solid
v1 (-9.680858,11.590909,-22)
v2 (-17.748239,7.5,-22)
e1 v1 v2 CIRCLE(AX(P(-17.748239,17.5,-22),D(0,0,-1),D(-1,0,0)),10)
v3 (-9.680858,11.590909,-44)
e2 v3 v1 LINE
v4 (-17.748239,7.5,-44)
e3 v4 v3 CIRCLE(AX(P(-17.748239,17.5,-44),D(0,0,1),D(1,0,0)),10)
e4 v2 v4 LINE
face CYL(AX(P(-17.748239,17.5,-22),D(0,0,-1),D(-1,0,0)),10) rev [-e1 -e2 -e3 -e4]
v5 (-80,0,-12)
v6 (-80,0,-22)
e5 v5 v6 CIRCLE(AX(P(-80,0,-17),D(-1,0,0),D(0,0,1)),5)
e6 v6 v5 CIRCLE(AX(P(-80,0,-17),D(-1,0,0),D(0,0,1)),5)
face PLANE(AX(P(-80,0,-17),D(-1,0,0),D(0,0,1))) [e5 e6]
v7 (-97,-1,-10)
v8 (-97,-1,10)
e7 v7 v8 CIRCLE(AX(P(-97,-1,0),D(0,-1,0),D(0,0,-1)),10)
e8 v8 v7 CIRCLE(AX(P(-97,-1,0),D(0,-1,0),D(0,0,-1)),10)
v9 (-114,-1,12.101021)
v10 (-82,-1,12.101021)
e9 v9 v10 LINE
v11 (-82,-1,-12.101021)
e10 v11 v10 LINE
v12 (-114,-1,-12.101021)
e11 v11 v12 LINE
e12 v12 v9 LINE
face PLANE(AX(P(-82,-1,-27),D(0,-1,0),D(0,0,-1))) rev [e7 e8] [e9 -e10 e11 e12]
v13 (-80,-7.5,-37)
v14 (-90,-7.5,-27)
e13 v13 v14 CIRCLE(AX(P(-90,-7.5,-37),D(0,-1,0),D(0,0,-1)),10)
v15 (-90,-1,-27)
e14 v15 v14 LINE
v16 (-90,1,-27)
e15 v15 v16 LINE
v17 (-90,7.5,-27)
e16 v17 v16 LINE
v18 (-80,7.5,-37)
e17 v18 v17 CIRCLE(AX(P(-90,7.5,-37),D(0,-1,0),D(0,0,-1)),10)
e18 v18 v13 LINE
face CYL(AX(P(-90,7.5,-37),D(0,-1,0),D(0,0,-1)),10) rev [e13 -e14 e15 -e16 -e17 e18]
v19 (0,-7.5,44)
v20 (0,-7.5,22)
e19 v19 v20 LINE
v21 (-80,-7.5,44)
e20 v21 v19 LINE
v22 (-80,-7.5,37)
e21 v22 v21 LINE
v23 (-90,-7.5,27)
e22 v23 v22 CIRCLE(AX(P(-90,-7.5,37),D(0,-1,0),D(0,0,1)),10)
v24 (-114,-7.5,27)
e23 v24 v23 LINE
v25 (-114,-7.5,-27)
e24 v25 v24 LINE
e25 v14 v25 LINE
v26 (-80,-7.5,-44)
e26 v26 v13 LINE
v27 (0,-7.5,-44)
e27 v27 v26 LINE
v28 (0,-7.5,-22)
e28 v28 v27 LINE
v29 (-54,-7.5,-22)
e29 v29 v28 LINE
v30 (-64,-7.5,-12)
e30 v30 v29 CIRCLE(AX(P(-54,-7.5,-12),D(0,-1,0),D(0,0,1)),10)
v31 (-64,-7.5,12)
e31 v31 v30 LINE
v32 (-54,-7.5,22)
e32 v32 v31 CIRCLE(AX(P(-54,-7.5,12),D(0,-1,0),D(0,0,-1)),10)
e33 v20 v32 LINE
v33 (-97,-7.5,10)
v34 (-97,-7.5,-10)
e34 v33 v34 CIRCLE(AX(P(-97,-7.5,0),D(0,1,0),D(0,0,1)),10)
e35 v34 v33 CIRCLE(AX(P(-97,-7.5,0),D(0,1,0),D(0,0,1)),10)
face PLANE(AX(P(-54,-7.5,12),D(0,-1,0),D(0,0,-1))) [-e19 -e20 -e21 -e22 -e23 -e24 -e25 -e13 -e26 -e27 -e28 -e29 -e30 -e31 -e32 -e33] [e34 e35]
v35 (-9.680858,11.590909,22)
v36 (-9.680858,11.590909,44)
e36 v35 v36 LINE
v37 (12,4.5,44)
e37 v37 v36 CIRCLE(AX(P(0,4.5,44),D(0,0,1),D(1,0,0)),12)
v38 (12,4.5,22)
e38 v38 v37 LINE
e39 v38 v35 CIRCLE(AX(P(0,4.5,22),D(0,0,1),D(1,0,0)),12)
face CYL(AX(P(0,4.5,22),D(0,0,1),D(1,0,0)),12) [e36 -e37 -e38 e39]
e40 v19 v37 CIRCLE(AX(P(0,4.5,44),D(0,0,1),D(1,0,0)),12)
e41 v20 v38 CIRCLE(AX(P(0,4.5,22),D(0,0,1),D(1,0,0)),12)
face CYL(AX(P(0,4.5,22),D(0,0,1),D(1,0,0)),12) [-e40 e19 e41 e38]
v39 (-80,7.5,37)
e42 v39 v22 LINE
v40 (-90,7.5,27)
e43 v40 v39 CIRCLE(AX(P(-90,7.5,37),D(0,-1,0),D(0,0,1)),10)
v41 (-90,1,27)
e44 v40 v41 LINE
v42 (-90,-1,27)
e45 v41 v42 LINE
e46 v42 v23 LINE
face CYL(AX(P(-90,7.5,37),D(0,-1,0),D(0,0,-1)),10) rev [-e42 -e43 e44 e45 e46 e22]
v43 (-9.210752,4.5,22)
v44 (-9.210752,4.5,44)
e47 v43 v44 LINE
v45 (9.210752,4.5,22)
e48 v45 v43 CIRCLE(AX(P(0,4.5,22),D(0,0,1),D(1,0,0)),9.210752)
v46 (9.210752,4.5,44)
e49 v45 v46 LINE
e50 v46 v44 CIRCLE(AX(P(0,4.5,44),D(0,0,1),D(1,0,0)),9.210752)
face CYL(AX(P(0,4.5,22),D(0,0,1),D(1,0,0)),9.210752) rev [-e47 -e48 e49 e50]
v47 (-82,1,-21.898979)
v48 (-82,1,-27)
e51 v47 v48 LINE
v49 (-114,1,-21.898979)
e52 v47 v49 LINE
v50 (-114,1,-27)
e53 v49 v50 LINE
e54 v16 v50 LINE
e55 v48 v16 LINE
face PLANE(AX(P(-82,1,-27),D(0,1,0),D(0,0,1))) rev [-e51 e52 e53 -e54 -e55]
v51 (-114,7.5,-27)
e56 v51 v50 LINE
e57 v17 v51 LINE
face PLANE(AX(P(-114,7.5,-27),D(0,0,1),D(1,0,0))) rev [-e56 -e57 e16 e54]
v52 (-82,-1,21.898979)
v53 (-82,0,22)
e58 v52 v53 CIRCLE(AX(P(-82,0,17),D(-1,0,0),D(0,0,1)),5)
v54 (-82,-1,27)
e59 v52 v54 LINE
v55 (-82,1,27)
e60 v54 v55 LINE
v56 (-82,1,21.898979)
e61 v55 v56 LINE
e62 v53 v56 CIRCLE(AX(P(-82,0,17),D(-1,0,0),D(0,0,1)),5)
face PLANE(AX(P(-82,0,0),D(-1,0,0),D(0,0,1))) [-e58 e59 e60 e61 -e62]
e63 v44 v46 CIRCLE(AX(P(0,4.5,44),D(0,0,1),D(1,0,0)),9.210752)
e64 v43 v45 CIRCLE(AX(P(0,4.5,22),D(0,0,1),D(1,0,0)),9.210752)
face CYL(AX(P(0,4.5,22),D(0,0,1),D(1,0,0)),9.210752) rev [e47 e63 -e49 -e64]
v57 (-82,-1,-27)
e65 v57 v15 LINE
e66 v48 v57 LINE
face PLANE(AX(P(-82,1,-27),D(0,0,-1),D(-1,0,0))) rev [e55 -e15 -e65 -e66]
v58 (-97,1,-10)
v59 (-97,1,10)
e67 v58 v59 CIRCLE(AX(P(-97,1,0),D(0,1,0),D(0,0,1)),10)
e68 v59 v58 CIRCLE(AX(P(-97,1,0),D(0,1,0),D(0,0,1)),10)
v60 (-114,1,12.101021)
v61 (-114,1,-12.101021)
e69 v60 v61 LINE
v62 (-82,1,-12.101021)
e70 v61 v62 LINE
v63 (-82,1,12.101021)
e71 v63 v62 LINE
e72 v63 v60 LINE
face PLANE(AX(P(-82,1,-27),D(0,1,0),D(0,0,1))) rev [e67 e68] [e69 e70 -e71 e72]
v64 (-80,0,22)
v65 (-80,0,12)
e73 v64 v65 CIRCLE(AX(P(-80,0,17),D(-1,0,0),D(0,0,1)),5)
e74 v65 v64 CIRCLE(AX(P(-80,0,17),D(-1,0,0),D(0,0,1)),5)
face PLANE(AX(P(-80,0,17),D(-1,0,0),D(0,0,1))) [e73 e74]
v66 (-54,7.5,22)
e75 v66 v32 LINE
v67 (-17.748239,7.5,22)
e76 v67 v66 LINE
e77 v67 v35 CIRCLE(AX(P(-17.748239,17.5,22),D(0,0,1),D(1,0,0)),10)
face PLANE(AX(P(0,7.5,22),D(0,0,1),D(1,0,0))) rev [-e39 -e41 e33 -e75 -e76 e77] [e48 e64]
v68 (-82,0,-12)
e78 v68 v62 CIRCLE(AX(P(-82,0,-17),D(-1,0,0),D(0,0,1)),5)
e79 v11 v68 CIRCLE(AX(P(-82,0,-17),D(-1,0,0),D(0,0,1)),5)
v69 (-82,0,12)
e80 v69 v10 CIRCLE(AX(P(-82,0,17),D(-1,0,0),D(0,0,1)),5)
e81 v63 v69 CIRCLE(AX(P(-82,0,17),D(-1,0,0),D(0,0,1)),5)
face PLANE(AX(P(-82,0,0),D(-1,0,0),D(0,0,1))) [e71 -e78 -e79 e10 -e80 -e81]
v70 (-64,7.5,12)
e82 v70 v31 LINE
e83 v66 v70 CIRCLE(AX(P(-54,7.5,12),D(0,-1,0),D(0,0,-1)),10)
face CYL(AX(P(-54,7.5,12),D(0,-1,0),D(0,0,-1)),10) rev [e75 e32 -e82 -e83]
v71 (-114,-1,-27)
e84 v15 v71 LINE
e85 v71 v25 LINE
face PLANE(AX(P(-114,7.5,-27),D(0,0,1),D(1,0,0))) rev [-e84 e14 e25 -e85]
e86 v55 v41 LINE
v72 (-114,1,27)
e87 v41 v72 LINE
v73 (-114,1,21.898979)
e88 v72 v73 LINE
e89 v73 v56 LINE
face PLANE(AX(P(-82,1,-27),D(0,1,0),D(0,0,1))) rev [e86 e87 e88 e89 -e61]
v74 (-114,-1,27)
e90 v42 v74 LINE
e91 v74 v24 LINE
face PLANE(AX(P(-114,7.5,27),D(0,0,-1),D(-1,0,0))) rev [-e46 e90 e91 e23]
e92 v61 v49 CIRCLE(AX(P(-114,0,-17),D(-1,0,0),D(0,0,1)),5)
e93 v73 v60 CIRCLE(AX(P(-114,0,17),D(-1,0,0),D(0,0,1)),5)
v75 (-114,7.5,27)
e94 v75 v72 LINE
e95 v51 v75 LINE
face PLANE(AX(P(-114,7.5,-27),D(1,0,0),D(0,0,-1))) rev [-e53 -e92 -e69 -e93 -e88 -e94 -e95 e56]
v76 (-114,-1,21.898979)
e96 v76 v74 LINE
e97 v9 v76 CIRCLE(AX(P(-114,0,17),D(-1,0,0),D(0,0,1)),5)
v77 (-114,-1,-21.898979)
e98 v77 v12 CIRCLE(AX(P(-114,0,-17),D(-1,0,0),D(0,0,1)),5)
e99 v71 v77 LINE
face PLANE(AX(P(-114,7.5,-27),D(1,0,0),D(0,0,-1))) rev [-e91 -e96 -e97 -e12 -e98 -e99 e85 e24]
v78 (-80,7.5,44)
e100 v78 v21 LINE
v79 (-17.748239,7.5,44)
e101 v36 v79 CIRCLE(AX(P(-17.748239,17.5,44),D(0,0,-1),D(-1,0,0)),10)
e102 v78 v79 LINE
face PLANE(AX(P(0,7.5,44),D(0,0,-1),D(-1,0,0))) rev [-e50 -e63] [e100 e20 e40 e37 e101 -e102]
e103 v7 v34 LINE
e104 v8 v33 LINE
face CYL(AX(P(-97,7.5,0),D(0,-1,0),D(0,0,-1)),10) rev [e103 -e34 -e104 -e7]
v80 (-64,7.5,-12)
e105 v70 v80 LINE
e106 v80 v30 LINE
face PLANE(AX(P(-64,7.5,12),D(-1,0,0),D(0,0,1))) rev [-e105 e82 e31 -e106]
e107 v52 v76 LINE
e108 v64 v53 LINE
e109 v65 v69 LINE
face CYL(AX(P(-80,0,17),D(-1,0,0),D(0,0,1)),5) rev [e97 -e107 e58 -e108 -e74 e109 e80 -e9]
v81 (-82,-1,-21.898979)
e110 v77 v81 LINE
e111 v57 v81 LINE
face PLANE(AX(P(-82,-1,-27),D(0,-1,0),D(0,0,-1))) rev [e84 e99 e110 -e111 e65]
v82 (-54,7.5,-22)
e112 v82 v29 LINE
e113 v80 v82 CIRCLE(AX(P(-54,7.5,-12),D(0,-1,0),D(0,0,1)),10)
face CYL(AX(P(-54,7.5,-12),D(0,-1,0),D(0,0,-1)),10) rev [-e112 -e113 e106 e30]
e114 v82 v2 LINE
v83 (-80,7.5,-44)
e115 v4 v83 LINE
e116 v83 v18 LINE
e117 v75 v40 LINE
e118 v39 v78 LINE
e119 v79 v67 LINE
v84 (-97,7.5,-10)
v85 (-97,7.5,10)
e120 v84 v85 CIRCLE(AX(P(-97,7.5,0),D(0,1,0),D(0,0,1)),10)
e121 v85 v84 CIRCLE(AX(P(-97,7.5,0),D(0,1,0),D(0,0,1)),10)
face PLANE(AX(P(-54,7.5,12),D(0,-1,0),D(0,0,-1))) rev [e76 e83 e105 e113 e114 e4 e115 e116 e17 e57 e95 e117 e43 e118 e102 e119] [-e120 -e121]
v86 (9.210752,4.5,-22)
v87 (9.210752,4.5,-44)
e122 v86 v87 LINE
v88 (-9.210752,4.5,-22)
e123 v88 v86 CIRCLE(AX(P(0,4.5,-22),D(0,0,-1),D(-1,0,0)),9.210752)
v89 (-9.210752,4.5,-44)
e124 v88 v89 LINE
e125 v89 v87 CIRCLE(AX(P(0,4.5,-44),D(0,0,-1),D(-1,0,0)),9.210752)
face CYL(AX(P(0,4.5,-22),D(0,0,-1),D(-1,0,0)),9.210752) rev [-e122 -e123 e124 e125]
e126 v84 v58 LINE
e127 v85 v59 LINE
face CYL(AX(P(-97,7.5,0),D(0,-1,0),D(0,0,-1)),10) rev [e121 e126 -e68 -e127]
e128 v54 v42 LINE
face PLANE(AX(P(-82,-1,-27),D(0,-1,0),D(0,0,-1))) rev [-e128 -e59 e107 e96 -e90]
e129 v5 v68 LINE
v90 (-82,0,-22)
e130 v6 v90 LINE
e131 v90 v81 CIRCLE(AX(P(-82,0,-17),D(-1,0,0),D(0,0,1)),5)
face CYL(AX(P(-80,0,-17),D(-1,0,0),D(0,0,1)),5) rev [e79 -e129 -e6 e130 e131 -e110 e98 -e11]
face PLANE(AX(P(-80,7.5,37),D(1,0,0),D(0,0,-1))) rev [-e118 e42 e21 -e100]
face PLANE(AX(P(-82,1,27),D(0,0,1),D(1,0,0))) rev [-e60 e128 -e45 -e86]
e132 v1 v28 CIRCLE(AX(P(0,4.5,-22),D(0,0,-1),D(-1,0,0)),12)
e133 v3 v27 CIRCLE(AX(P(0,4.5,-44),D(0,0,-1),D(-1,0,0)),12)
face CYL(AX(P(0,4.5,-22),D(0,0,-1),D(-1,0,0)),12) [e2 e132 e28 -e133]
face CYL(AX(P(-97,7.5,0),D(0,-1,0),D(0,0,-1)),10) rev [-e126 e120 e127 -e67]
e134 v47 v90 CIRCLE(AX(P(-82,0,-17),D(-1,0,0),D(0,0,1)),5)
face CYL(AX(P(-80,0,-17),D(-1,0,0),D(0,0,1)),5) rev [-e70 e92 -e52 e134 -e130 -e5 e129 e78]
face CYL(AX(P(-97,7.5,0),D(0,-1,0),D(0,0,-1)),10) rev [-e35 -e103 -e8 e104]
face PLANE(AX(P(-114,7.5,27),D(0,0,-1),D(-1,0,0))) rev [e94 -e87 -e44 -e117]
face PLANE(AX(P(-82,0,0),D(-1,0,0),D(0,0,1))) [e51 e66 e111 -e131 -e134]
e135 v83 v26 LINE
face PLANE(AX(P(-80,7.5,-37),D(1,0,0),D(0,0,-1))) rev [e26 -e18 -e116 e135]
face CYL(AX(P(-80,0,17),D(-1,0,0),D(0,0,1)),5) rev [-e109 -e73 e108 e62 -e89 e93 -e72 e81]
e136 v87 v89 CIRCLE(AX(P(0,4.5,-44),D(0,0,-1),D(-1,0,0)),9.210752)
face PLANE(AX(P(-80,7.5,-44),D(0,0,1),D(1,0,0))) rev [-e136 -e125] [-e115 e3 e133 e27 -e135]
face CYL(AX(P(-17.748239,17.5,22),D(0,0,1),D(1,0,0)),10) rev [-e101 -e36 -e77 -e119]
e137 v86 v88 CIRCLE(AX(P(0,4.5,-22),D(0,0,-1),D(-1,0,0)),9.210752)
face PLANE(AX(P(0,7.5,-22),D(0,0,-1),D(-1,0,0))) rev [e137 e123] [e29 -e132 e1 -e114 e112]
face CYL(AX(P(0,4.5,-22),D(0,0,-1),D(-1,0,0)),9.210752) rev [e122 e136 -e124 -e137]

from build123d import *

# Parameters (mm, degrees)
BASE_PLATE_SKETCH_R     = 10
BASE_PLATE_DEPTH        = 7.5
KNUCKLE_A_SKETCH_R      = 12
KNUCKLE_A_SKETCH_R_2    = 9
KNUCKLE_A_DEPTH         = 22
KNUCKLE_A_BORE_SKETCH_R = 9.21075175
KNUCKLE_A_BORE_DEPTH    = 22
KNUCKLE_A_BLEND_R10_R   = 10
KNUCKLE_START           = -22
KNUCKLE_B_SKETCH_R      = 12
KNUCKLE_B_SKETCH_R_2    = 9.21075175
KNUCKLE_B_DEPTH         = 22
KNUCKLE_B_BORE_SKETCH_R = 9.21075175
KNUCKLE_B_BORE_DEPTH    = 22
KNUCKLE_B_BLEND_R10_R   = 10
GROOVE_CUT_SKETCH_W     = 54
GROOVE_CUT_SKETCH_H     = 2
GROOVE_CUT_DEPTH        = 32
HOLE_CUT_SKETCH_R       = 5
HOLE_CUT_DEPTH          = 34


with BuildPart() as part:
    # Base Plate Sketch → Base Plate (new, symmetric)
    with BuildSketch(Plane(origin=(0, 0, 0), x_dir=(1, 0, 0), z_dir=(0, 1, 0))):
        with BuildLine():
            Line((0, 44), (0, 22))
            Line((0, 22), (-54, 22))
            ThreePointArc((-54, 22), (-61.071067812, 19.071067812), (-64, 12))
            Line((-64, 12), (-64, -12))
            ThreePointArc((-64, -12), (-61.071067812, -19.071067812), (-54, -22))
            Line((-54, -22), (0, -22))
            Line((0, -22), (0, -44))
            Line((0, -44), (-64, -44))
            Line((-64, -44), (-80, -44))
            Line((-80, -44), (-80, -37))
            ThreePointArc((-80, -37), (-82.928932188, -29.928932188), (-90, -27))
            Line((-90, -27), (-114, -27))
            Line((-114, -27), (-114, 27))
            Line((-114, 27), (-90, 27))
            ThreePointArc((-90, 27), (-82.928932188, 29.928932188), (-80, 37))
            Line((-80, 37), (-80, 44))
            Line((-80, 44), (-64, 44))
            Line((-64, 44), (0, 44))
        make_face()
        with Locations(Location((-97, 0, 0), (0, 0, 270))):
            Circle(BASE_PLATE_SKETCH_R, mode=Mode.SUBTRACT)
    extrude(amount=BASE_PLATE_DEPTH, both=True)

    # Knuckle A Sketch → Knuckle A (add)
    with BuildSketch(Plane.XY.offset(44)):
        with Locations((0, 4.5)):
            Circle(KNUCKLE_A_SKETCH_R)
        with Locations((0, 4.5)):
            Circle(KNUCKLE_A_SKETCH_R_2, mode=Mode.SUBTRACT)
    extrude(amount=-KNUCKLE_A_DEPTH)

    # Knuckle A Bore Sketch → Knuckle A Bore (cut)
    with BuildSketch(Plane.XY.offset(44)):
        with Locations((0, 4.5)):
            Circle(KNUCKLE_A_BORE_SKETCH_R)
    extrude(amount=-KNUCKLE_A_BORE_DEPTH, mode=Mode.SUBTRACT)

    # Knuckle A Blend R10
    knuckle_a_blend_r10_edges = [part.edges().sort_by_distance(p)[0] for p in [
        (-11.618950039, 7.5, 33),
    ]]
    fillet(knuckle_a_blend_r10_edges, radius=KNUCKLE_A_BLEND_R10_R)

    # Knuckle B Sketch → Knuckle B (add)
    with BuildSketch(Plane(origin=(0, 0, -44), x_dir=(-1, 0, 0), z_dir=(0, 0, -1)).offset(KNUCKLE_START)):
        with Locations((0, 4.5)):
            Circle(KNUCKLE_B_SKETCH_R)
        with Locations(Location((0, 4.5, 0), (0, 0, 180))):
            Circle(KNUCKLE_B_SKETCH_R_2, mode=Mode.SUBTRACT)
    extrude(amount=KNUCKLE_B_DEPTH)

    # Knuckle B Bore Sketch → Knuckle B Bore (cut)
    with BuildSketch(Plane(origin=(0, 0, -44), x_dir=(-1, 0, 0), z_dir=(0, 0, -1)).offset(KNUCKLE_START)):
        with Locations(Location((0, 4.5, 0), (0, 0, 180))):
            Circle(KNUCKLE_B_BORE_SKETCH_R)
    extrude(amount=KNUCKLE_B_BORE_DEPTH, mode=Mode.SUBTRACT)

    # Knuckle B Blend R10
    knuckle_b_blend_r10_edges = [part.edges().sort_by_distance(p)[0] for p in [
        (-11.618950039, 7.5, -33),
    ]]
    fillet(knuckle_b_blend_r10_edges, radius=KNUCKLE_B_BLEND_R10_R)

    # Groove Cut Sketch → Groove Cut (cut)
    with BuildSketch(Plane.ZY.offset(114)):
        Rectangle(GROOVE_CUT_SKETCH_W, GROOVE_CUT_SKETCH_H)
    extrude(amount=-GROOVE_CUT_DEPTH, mode=Mode.SUBTRACT)

    # Hole Cut Sketch → Hole Cut (cut)
    with BuildSketch(Plane.ZY.offset(114)):
        with Locations((-17, 0)):
            Circle(HOLE_CUT_SKETCH_R)
        with Locations((17, 0)):
            Circle(HOLE_CUT_SKETCH_R)
    extrude(amount=-HOLE_CUT_DEPTH, mode=Mode.SUBTRACT)


solid = part.part
